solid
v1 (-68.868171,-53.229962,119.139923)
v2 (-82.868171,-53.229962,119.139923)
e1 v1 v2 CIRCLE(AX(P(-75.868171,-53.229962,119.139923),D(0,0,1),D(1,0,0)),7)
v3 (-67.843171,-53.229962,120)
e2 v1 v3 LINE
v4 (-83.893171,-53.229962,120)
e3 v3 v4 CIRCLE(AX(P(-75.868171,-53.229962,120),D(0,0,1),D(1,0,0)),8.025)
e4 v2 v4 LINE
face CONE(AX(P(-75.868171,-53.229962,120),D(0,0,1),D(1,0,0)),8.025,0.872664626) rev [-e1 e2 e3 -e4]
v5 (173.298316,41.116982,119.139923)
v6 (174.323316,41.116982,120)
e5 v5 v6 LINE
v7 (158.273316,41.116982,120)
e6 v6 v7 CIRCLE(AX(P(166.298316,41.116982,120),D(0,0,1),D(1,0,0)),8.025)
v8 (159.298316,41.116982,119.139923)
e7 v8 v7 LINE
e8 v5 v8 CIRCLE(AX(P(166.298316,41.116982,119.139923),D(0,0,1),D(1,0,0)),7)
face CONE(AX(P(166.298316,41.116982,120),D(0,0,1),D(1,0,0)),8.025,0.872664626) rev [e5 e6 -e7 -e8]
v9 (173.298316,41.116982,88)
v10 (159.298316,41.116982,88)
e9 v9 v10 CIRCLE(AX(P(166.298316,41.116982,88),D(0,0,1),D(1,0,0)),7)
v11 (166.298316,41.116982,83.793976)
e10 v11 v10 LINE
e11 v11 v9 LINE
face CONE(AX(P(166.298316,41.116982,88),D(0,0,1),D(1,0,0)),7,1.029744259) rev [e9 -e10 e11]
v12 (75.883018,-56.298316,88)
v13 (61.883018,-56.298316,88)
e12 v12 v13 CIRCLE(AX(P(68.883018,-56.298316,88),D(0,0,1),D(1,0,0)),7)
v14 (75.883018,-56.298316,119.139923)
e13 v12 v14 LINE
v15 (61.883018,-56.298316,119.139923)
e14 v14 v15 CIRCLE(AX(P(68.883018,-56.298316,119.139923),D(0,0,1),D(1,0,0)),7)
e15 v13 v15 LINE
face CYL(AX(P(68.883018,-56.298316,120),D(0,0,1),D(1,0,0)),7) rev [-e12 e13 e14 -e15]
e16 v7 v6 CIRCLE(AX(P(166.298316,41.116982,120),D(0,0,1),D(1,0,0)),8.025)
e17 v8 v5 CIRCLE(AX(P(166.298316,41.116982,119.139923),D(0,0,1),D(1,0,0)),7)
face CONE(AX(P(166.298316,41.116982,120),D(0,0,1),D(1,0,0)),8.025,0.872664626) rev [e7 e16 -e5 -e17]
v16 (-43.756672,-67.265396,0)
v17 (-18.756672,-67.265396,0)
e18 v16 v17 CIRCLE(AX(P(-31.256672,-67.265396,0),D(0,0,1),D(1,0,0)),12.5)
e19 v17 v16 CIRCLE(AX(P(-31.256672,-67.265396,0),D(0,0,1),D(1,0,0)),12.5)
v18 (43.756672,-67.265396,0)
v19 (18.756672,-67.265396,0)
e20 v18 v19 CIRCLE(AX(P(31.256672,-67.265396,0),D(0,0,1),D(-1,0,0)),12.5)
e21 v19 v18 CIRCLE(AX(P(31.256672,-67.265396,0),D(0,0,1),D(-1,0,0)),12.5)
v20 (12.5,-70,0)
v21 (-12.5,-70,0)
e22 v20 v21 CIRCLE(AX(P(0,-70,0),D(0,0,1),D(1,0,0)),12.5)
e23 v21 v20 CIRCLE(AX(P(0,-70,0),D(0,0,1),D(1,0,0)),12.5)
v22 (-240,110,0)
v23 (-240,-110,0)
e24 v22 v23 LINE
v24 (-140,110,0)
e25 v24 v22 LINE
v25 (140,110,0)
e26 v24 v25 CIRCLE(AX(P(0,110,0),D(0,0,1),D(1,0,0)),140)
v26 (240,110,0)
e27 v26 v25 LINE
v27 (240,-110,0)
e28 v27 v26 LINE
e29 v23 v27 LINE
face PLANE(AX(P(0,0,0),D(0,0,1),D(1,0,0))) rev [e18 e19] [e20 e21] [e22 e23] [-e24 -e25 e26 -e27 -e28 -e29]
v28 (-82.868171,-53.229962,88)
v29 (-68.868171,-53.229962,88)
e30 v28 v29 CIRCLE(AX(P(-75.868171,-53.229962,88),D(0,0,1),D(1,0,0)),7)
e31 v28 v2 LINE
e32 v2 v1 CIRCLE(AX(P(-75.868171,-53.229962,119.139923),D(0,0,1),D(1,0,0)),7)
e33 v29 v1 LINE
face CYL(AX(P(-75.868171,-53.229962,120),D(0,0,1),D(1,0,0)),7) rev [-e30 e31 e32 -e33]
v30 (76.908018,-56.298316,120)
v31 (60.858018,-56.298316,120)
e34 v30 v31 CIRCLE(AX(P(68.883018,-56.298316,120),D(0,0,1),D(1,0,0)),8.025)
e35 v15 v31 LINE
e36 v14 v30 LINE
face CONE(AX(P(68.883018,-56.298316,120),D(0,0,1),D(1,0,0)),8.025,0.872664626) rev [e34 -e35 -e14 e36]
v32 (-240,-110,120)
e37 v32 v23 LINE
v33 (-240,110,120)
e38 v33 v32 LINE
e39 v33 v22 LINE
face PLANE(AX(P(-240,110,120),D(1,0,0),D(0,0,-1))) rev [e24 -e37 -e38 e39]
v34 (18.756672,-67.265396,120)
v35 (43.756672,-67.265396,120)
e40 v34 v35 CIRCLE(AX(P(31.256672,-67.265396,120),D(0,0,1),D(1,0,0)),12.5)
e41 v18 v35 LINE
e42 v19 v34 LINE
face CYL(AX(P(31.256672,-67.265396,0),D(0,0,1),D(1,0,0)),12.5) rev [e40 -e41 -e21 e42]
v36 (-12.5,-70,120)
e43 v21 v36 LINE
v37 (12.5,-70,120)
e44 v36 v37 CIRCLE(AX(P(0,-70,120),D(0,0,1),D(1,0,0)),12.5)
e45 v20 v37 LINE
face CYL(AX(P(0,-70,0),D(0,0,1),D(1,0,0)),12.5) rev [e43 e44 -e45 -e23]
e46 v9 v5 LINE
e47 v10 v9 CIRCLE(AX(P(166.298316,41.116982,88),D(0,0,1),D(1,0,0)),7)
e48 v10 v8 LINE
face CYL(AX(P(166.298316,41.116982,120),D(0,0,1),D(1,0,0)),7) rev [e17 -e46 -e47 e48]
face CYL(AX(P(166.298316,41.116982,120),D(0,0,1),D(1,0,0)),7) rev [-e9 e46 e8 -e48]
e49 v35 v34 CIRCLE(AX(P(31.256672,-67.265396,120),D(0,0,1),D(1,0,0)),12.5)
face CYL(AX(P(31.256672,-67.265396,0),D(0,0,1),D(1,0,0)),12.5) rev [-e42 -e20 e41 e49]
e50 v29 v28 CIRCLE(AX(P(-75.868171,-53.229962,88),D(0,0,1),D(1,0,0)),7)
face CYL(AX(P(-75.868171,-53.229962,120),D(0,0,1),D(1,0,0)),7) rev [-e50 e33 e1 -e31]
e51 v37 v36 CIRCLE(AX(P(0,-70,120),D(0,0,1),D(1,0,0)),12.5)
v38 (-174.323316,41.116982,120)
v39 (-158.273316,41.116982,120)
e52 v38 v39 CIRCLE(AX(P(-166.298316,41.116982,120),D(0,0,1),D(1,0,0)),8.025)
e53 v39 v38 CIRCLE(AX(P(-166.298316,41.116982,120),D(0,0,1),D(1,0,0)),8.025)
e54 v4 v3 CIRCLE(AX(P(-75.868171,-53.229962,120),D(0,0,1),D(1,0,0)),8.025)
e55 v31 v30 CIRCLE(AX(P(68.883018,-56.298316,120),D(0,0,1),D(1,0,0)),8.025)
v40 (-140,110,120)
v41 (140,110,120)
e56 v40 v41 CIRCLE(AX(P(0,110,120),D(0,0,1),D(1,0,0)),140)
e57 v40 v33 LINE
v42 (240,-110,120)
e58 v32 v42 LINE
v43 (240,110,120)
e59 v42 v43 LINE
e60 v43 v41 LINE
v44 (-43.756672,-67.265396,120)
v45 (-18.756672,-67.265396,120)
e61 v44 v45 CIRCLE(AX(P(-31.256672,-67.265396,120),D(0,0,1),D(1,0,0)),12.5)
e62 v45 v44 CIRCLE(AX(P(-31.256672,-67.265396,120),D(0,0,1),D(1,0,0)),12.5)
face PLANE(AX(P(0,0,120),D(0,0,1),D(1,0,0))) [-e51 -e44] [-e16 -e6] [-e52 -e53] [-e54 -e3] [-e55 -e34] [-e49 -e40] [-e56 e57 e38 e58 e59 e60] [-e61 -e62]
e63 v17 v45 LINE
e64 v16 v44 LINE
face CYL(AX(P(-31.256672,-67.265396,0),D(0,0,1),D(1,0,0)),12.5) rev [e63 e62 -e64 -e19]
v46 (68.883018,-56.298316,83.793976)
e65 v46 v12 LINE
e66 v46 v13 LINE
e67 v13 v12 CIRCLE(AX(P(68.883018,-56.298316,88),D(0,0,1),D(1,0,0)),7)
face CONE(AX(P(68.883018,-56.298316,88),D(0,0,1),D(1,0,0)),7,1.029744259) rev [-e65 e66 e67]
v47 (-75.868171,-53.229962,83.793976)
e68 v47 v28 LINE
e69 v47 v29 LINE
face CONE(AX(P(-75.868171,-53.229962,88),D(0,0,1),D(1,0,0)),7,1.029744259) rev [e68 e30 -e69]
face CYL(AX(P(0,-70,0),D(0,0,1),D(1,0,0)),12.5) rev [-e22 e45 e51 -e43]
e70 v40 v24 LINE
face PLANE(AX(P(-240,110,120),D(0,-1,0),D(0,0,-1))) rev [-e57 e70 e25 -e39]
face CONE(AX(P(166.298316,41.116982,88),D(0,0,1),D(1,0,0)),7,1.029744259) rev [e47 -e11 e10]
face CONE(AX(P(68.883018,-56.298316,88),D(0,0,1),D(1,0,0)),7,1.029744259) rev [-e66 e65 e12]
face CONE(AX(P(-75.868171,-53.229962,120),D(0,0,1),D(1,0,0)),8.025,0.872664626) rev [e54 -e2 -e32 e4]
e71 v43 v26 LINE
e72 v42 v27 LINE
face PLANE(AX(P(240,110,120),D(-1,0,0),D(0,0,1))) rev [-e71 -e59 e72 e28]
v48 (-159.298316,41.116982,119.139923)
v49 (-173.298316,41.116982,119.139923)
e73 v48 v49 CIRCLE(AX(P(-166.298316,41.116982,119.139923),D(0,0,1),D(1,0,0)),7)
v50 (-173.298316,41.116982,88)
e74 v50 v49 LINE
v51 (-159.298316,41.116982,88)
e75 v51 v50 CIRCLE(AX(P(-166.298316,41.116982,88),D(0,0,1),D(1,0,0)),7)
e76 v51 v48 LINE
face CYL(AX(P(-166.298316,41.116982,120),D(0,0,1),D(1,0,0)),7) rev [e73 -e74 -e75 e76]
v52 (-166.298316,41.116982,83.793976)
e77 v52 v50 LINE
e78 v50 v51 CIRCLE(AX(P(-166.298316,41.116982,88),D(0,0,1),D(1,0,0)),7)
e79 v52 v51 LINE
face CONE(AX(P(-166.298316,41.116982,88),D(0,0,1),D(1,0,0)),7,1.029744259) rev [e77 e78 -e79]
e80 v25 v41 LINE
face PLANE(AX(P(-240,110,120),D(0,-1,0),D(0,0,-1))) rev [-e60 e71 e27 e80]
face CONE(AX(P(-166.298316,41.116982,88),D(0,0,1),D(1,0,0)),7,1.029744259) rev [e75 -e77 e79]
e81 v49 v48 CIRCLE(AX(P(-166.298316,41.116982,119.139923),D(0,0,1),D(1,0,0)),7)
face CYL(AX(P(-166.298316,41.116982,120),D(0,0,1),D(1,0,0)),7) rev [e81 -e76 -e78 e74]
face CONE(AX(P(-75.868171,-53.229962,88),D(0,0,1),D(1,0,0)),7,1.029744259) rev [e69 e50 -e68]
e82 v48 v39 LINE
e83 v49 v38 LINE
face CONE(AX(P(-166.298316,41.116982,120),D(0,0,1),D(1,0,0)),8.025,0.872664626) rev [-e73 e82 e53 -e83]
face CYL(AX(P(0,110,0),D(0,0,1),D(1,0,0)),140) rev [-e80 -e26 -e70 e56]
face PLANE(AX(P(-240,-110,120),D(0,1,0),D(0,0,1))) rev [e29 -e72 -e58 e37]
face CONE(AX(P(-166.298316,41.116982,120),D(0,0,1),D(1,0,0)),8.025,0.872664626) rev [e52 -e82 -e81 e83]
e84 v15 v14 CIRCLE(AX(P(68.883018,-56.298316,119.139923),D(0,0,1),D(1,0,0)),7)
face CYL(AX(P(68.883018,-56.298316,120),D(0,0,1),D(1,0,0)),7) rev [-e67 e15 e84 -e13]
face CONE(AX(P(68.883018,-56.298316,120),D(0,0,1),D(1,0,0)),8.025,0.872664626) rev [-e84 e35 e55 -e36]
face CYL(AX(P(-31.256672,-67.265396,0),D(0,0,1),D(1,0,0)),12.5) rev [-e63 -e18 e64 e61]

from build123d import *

# Parameters (mm, degrees)
SKETCH1_W                    = 480
SKETCH1_H                    = 220
BOSS_EXTRUDE1_DEPTH          = 120
CUT_EXTRUDE1_DEPTH           = 291
CUT_EXTRUDE1_DEPTH_BACK      = 291
SKETCH2_R                    = 140
CUT_EXTRUDE2_DEPTH           = 291
CUT_EXTRUDE2_DEPTH_BACK      = 291
SKETCH4_R                    = 12.5
M16_TAPPED_HOLE1_D           = 14
M16_TAPPED_HOLE1_DEPTH       = 32
M16_TAPPED_HOLE1_CSINK_D     = 16.05
M16_TAPPED_HOLE1_CSINK_ANGLE = 100
M16_TAPPED_HOLE1_TIP         = 4.206024333


with BuildPart() as part:
    # Sketch1 → Boss-Extrude1 (new body)
    with BuildSketch(Plane.XY):
        Rectangle(SKETCH1_W, SKETCH1_H)
    extrude(amount=BOSS_EXTRUDE1_DEPTH)

    # Sketch2 → Cut-Extrude1 (cut, two sides: drawn at the far end of the back side and taken through both)
    with BuildSketch(Plane.XY.offset(120).offset(-CUT_EXTRUDE1_DEPTH_BACK)):
        with Locations((0, 110)):
            Circle(SKETCH2_R)
    extrude(amount=CUT_EXTRUDE1_DEPTH + CUT_EXTRUDE1_DEPTH_BACK, mode=Mode.SUBTRACT)

    # Sketch4 → Cut-Extrude2 (cut, two sides: drawn at the far end of the back side and taken through both)
    with BuildSketch(Plane.XY.offset(120).offset(-CUT_EXTRUDE2_DEPTH_BACK)):
        with Locations((0, -70)):
            Circle(SKETCH4_R)
        with Locations((-31.25667198, -67.265395542)):
            Circle(SKETCH4_R)
        with Locations((31.25667198, -67.265395542)):
            Circle(SKETCH4_R)
    extrude(amount=CUT_EXTRUDE2_DEPTH + CUT_EXTRUDE2_DEPTH_BACK, mode=Mode.SUBTRACT)

    # M16 Tapped Hole1
    with Locations(Plane.XY.offset(120)):
        with Locations((-166.298315852, 41.116982174), (166.298315852, 41.116982174), (68.883017826, -56.298315852), (-75.868170831, -53.229962491)):
            CounterSinkHole(M16_TAPPED_HOLE1_D / 2, M16_TAPPED_HOLE1_CSINK_D / 2, depth=M16_TAPPED_HOLE1_DEPTH, counter_sink_angle=M16_TAPPED_HOLE1_CSINK_ANGLE)
            with Locations((0, 0, -(M16_TAPPED_HOLE1_DEPTH + M16_TAPPED_HOLE1_TIP / 2))):  # 118° drill point
                Cone(0, M16_TAPPED_HOLE1_D / 2, M16_TAPPED_HOLE1_TIP, mode=Mode.SUBTRACT)


solid = part.part
